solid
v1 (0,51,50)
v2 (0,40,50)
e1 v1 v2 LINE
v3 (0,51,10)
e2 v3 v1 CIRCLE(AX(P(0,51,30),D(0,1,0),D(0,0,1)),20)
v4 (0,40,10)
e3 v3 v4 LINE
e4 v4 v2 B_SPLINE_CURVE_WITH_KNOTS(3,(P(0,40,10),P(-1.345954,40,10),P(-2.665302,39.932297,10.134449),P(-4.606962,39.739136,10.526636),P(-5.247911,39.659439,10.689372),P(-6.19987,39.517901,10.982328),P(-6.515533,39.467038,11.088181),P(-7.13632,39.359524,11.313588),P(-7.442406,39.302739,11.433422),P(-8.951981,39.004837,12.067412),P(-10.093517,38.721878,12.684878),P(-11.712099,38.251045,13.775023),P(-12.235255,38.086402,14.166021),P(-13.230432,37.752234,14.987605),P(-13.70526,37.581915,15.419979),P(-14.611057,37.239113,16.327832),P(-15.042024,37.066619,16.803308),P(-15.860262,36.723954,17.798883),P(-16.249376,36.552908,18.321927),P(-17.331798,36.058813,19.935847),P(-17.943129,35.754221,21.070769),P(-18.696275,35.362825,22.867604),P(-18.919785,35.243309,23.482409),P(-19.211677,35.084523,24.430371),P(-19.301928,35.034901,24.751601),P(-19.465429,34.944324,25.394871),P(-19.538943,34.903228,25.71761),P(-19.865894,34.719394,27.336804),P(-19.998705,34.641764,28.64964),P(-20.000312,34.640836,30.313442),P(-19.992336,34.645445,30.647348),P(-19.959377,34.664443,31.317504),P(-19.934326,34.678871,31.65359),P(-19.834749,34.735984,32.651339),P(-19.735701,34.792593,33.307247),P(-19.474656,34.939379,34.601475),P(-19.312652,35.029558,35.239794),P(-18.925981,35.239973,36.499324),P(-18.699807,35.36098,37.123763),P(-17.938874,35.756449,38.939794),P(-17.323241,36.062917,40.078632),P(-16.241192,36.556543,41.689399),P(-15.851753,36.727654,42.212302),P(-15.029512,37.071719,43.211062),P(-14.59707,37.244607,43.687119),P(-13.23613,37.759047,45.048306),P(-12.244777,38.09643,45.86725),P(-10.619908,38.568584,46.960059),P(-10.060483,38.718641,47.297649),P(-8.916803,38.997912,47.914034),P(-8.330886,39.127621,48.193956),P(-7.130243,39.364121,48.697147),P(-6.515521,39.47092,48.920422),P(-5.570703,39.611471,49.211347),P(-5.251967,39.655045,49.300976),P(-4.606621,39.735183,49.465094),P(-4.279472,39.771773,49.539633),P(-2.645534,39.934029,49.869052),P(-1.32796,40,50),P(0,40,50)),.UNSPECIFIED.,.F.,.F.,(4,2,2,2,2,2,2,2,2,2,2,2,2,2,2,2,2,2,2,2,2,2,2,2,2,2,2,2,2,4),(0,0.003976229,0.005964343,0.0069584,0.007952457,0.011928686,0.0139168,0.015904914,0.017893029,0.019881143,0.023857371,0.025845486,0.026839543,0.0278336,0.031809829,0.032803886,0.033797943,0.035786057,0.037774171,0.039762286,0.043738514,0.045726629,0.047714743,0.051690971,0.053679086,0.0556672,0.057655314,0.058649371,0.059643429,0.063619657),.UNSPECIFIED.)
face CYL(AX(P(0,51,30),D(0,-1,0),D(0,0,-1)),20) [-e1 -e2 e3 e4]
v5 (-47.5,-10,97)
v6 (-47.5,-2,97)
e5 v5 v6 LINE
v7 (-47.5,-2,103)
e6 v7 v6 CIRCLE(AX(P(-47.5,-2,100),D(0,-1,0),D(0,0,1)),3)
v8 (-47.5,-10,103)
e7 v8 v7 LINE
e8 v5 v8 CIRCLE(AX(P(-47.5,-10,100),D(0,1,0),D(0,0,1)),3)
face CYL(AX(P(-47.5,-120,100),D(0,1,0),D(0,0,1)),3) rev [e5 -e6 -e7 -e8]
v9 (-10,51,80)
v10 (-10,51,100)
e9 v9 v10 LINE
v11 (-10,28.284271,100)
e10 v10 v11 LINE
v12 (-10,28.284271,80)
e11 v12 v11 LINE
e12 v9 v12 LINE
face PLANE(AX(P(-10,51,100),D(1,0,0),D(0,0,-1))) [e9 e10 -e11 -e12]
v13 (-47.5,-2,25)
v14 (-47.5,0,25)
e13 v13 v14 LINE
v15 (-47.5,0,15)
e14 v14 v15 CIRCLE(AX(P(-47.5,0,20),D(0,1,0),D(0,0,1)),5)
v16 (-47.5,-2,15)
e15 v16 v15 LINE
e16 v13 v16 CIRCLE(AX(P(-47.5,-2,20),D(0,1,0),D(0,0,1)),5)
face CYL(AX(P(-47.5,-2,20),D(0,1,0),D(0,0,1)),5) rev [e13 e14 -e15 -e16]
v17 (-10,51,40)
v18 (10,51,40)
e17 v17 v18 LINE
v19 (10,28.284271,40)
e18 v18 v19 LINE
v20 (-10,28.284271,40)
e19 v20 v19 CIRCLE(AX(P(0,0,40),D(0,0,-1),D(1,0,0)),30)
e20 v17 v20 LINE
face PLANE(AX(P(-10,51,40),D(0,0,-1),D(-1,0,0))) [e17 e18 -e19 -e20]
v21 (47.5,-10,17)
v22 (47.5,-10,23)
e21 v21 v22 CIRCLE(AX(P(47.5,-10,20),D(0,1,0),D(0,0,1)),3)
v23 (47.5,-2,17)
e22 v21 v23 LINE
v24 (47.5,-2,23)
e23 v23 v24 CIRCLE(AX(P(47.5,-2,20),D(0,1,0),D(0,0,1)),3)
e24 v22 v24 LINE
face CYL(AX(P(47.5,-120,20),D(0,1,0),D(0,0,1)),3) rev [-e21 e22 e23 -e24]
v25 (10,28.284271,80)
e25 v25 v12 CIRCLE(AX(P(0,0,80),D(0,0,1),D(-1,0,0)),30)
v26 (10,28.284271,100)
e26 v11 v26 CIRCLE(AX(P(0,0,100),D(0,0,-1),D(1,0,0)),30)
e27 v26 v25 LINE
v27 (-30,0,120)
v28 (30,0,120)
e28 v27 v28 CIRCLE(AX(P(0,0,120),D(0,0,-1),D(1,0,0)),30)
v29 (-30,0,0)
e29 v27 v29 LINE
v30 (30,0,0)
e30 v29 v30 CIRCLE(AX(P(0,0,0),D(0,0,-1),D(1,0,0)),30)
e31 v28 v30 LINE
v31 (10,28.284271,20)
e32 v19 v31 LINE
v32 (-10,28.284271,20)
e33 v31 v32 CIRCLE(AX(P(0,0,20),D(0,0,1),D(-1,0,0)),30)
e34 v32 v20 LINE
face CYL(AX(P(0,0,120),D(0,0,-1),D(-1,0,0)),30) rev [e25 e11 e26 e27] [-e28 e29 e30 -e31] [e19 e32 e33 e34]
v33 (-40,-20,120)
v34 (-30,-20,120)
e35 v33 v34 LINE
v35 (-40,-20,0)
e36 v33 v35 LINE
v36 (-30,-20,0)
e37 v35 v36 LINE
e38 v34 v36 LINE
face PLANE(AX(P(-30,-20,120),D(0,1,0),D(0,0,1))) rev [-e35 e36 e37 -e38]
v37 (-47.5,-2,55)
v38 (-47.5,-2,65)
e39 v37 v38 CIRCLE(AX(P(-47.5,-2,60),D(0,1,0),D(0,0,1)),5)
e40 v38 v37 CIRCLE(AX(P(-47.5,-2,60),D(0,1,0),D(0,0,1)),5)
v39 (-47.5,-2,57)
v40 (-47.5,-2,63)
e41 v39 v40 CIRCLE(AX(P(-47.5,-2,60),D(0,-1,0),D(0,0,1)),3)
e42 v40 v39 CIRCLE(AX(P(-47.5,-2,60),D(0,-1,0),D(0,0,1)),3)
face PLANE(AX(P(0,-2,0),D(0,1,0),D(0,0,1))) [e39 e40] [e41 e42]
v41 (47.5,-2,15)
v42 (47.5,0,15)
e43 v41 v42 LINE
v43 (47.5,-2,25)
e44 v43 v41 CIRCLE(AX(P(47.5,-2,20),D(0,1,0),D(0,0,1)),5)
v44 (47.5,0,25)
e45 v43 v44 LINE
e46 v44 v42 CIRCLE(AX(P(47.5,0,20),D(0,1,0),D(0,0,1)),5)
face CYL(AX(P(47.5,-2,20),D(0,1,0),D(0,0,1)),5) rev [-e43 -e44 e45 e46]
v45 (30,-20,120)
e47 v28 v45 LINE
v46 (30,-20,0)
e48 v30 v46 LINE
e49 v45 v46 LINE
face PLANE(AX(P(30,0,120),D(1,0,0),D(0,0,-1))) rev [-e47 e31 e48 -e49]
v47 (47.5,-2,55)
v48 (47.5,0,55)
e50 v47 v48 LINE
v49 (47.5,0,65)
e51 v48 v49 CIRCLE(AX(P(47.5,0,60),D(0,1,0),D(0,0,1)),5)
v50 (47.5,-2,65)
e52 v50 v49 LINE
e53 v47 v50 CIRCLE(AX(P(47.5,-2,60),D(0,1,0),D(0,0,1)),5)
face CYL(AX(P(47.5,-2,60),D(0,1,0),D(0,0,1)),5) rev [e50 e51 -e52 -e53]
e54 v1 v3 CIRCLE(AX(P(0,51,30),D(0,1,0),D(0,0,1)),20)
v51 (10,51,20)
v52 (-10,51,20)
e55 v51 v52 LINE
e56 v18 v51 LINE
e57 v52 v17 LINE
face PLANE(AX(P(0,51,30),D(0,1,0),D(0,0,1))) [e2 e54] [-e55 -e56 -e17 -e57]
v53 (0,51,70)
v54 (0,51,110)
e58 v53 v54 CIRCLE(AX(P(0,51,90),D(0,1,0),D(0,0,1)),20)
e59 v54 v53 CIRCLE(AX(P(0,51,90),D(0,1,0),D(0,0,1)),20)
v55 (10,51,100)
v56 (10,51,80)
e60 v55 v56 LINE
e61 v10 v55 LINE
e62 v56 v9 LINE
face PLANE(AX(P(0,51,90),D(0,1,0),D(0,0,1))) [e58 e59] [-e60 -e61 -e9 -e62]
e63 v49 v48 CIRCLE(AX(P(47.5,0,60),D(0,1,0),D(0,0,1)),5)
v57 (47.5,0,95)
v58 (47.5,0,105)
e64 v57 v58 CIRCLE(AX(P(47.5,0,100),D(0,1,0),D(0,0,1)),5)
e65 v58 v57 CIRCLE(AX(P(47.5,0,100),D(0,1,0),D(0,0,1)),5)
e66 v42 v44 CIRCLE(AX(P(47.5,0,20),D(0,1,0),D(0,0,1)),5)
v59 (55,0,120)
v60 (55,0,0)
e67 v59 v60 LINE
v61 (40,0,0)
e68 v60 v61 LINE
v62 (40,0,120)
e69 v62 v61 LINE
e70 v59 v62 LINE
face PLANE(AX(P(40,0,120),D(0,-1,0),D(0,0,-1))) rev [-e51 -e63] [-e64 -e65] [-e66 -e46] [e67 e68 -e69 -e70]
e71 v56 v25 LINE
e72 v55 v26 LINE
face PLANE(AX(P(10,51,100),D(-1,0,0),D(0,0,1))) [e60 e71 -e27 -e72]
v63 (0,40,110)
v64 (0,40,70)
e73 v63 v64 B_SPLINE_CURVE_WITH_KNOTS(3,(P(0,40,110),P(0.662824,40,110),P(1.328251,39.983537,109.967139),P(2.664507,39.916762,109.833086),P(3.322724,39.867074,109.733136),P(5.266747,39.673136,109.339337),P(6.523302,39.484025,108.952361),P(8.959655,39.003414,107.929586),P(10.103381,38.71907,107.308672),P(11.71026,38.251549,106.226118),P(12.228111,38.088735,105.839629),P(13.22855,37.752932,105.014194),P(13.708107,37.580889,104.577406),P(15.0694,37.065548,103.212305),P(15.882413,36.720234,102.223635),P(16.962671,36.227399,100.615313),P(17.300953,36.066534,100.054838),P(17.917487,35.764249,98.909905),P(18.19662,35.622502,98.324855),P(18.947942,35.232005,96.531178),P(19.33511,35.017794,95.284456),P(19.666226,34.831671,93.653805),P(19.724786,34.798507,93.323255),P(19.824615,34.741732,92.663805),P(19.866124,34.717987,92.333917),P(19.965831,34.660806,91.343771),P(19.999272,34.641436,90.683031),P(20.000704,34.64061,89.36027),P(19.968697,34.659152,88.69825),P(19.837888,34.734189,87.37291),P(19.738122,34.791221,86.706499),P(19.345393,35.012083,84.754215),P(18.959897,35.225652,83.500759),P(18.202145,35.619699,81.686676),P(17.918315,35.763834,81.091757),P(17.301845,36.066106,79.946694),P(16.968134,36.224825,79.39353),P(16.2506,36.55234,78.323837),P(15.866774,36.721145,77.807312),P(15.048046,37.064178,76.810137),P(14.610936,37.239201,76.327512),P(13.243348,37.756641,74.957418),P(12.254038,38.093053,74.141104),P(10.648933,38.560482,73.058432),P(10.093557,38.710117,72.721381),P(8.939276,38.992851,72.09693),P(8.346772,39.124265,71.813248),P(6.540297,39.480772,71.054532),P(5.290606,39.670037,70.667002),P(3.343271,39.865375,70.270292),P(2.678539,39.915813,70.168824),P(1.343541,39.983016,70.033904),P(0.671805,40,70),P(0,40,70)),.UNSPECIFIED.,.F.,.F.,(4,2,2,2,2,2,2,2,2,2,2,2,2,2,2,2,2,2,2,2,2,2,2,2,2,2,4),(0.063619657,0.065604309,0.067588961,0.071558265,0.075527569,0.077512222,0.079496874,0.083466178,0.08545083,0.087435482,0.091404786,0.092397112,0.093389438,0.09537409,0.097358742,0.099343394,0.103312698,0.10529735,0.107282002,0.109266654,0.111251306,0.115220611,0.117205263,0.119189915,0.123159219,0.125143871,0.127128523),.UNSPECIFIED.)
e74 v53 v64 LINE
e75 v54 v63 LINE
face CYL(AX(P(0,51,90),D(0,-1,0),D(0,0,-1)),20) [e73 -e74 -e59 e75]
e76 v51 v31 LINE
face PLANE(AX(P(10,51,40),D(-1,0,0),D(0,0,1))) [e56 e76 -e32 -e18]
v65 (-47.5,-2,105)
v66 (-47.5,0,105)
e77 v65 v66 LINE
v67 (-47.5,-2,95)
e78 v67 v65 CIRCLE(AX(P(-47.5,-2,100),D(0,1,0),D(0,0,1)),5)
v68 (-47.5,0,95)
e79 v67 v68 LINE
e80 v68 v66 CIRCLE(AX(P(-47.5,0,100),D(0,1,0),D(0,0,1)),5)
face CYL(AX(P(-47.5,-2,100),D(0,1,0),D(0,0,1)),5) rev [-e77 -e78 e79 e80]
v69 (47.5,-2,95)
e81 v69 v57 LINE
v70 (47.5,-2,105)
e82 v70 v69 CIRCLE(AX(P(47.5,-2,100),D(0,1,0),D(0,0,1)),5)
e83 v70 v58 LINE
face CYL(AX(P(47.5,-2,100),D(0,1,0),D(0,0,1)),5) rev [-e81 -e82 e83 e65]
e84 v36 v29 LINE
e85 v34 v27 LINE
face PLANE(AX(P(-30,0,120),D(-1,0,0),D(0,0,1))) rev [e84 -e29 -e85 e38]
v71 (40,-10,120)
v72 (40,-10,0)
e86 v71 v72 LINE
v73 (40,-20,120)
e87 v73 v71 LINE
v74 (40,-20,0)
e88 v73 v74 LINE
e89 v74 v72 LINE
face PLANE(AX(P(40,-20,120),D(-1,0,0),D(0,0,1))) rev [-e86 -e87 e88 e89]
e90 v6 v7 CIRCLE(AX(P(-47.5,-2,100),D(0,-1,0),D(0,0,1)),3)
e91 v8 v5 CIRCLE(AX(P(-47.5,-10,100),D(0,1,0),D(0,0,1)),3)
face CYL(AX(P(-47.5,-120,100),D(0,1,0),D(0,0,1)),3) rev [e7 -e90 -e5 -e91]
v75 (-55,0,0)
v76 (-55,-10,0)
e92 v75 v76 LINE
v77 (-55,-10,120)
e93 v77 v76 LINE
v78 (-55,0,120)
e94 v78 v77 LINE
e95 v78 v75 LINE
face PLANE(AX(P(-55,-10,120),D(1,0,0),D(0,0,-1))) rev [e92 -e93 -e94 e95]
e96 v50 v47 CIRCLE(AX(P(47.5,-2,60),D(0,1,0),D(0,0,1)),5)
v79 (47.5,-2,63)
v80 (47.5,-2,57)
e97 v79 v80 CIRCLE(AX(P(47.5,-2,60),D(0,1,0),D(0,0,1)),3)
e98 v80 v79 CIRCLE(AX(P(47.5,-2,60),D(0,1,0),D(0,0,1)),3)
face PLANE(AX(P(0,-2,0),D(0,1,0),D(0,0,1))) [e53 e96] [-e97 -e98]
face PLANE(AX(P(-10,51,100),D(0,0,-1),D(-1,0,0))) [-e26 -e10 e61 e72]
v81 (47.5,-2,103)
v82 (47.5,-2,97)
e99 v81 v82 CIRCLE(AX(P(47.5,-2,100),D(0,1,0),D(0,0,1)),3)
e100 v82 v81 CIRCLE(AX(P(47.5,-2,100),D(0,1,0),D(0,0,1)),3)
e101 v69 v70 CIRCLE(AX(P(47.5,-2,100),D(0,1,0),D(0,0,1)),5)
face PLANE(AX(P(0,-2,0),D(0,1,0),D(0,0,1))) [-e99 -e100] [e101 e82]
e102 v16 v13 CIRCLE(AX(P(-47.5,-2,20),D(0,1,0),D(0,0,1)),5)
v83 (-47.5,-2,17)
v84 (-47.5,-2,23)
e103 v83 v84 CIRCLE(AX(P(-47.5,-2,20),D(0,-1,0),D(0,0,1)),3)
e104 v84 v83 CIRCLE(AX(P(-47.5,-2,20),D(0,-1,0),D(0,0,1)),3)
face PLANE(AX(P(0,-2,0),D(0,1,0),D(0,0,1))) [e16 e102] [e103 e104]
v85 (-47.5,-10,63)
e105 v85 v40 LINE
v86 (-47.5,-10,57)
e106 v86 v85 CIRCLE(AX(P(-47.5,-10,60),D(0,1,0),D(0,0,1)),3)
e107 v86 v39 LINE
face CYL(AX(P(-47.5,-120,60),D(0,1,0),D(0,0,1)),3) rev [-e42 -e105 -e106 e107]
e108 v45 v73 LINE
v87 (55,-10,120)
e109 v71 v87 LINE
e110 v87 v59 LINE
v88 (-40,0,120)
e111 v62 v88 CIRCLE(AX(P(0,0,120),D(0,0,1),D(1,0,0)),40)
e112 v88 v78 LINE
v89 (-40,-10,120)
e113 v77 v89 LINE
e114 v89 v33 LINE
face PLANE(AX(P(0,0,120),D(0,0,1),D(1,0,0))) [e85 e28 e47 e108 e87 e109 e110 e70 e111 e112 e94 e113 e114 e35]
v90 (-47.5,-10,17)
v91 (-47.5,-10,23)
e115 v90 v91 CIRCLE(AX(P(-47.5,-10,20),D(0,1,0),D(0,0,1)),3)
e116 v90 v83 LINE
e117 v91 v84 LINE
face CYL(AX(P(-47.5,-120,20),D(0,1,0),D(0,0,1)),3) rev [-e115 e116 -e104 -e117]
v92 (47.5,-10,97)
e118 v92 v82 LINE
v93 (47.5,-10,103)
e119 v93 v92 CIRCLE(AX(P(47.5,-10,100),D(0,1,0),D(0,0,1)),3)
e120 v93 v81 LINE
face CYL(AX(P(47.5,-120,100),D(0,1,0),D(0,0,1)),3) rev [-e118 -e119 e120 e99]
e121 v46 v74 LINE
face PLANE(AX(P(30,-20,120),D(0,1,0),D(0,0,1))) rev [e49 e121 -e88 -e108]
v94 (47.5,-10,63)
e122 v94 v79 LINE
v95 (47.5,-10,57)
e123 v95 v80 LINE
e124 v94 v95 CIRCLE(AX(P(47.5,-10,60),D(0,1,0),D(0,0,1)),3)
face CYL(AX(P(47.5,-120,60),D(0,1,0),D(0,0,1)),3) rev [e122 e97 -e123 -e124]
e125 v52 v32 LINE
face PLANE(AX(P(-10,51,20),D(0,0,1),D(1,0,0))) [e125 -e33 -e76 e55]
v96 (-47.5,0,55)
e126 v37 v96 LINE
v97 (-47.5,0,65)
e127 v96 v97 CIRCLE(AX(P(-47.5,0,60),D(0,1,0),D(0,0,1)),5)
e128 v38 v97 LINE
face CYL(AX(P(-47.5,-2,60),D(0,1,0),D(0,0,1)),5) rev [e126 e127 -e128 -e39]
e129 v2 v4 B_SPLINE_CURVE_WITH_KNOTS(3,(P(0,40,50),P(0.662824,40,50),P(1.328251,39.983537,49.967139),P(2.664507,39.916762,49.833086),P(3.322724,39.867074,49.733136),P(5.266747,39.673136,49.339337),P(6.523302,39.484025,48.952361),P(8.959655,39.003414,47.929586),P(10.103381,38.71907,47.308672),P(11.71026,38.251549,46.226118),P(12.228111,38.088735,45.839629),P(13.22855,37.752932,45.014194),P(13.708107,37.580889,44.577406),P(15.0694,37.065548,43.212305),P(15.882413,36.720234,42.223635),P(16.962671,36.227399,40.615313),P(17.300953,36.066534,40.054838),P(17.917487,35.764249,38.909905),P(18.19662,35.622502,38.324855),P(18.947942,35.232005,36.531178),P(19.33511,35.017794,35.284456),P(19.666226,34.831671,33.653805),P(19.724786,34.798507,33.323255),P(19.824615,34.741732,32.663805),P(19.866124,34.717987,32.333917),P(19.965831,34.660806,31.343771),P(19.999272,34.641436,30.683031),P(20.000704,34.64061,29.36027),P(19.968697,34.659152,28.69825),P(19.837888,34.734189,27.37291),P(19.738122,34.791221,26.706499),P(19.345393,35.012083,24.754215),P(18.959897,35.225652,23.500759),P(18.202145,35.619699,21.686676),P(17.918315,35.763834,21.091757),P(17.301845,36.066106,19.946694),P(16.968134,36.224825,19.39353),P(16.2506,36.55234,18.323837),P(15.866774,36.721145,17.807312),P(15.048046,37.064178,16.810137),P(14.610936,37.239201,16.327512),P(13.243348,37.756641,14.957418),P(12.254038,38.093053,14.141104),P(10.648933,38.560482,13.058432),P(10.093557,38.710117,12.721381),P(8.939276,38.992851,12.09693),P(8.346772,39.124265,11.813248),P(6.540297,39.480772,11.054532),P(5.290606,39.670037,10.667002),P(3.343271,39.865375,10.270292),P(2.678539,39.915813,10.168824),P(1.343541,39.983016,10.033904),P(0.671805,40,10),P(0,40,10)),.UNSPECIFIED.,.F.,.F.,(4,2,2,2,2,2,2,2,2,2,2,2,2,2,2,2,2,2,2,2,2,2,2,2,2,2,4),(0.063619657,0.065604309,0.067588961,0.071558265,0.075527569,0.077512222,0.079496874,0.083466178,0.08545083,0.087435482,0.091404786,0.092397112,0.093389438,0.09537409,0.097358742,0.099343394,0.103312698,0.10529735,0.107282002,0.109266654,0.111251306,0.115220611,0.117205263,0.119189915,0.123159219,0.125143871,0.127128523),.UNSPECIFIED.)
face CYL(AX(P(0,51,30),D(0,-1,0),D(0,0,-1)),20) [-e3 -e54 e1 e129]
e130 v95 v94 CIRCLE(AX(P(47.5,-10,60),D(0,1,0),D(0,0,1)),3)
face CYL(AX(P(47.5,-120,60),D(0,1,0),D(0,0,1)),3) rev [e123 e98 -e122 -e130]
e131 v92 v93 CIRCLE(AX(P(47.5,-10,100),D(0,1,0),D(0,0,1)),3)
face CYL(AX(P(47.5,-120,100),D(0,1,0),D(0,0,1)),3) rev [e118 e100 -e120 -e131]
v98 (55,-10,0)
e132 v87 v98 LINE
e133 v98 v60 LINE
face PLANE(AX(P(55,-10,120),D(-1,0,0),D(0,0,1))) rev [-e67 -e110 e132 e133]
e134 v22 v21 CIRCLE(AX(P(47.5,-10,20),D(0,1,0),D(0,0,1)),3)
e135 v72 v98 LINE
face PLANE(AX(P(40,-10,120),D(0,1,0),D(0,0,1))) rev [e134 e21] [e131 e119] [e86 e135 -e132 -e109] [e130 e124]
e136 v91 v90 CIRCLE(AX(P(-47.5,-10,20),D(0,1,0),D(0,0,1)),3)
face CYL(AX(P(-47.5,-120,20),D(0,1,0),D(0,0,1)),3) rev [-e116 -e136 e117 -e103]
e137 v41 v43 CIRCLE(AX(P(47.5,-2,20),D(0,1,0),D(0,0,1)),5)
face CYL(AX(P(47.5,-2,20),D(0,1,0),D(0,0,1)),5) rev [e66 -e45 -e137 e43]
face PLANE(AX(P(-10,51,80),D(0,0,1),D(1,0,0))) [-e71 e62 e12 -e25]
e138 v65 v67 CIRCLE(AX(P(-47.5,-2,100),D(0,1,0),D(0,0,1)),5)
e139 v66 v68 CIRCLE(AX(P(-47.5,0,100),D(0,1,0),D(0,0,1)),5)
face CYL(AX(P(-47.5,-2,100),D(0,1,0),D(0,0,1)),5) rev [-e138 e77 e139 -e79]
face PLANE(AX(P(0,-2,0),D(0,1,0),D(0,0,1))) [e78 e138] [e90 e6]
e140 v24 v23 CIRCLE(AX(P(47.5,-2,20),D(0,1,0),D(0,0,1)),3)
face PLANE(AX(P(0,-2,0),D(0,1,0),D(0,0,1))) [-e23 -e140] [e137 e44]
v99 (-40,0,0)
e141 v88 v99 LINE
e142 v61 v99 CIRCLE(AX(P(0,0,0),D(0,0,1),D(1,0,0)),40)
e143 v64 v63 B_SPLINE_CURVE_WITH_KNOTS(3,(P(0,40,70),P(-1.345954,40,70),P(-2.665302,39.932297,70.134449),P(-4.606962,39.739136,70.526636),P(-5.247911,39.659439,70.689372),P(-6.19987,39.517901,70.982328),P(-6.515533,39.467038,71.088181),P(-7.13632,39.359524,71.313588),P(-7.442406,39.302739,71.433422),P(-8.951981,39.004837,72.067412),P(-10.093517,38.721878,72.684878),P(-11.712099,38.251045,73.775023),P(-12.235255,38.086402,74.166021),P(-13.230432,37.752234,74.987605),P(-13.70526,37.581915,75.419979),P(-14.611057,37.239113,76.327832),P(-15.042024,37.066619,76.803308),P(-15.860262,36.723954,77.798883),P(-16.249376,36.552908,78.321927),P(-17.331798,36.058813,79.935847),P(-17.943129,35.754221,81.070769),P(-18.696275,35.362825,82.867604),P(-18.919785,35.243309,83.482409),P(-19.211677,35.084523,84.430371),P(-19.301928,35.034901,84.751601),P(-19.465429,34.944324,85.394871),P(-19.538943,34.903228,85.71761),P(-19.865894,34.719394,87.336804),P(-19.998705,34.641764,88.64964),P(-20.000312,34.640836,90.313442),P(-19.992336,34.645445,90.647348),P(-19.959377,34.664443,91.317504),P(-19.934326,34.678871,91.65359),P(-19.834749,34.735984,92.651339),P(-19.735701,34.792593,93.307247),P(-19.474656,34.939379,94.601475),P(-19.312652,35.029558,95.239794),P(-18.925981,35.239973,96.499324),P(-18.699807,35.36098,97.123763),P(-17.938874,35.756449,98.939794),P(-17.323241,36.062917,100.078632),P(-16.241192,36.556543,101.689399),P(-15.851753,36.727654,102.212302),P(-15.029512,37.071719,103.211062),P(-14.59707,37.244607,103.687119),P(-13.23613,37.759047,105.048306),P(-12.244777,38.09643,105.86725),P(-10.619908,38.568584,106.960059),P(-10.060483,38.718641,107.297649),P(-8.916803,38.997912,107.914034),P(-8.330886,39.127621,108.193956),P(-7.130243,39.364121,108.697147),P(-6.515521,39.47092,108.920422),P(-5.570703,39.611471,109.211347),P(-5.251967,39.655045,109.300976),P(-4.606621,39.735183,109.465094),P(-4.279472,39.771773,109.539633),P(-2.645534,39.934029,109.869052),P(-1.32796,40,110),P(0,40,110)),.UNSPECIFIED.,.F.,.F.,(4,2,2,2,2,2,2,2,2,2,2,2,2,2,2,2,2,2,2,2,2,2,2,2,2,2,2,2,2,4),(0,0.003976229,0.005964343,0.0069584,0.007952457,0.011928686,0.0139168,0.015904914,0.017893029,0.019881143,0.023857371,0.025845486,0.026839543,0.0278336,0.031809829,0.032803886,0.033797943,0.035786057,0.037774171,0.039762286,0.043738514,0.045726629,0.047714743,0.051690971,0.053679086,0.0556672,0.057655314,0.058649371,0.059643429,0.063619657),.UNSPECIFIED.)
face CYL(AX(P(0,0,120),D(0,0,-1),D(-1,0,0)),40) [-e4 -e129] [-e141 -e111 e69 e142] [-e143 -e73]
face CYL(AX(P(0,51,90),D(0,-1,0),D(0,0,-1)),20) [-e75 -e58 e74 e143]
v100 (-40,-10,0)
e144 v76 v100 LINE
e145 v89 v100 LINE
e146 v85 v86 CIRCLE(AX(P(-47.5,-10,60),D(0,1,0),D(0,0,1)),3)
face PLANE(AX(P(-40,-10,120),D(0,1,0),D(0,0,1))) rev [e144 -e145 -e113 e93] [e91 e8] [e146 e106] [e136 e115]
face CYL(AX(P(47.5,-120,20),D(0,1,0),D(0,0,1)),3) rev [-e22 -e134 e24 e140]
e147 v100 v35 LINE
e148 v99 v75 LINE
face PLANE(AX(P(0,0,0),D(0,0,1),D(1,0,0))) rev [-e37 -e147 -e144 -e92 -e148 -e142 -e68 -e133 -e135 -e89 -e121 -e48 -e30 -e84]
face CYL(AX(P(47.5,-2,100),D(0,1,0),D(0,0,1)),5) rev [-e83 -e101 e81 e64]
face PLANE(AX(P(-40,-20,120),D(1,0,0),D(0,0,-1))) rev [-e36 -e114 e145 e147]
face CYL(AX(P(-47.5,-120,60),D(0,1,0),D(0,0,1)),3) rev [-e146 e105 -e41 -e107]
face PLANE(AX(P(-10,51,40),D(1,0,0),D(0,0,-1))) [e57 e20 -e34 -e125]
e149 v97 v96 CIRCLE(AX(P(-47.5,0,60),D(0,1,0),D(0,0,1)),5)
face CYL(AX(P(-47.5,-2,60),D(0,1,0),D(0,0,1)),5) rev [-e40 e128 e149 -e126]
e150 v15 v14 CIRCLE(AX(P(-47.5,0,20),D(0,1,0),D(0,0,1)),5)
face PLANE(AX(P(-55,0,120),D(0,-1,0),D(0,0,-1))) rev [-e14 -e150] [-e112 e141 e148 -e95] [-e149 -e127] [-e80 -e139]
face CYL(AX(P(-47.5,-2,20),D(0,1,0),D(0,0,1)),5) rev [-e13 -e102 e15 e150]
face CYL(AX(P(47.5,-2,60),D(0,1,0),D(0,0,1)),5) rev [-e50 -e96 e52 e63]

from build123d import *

# Parameters (mm, degrees)
HALF_PIPE_CAP_BODY_DEPTH     = 120
MOUNTING_HOLES_SKETCH_R      = 3
MOUNTING_HOLES_6X_6_DEPTH    = 120
COUNTERBORE_SKETCH_R         = 5
COUNTERBORE_SKETCH_R_2       = 3
COUNTERBORES_6X_10X2_DEPTH   = 2
BOSS_SKETCH_R                = 20
BOSS_SKETCH_W                = 20
BOSS_SKETCH_H                = 20
TOP_BOSSES_2X_40_DEPTH       = 20
SQUARE_SOCKET_SKETCH_W       = 20
SQUARE_SOCKET_SKETCH_H       = 20
SQUARE_SOCKETS_2X20X20_DEPTH = 20


with BuildPart() as part:
    # Cap Profile Sketch → Half Pipe Cap Body (new body)
    with BuildSketch(Plane.XY):
        with BuildLine():
            Line((-55, 0), (-40, 0))
            ThreePointArc((-40, 0), (0, 40), (40, 0))
            Line((40, 0), (55, 0))
            Line((55, 0), (55, -10))
            Line((55, -10), (40, -10))
            Line((40, -10), (40, -20))
            Line((40, -20), (30, -20))
            Line((30, -20), (30, 0))
            ThreePointArc((30, 0), (0, 30), (-30, 0))
            Line((-30, 0), (-30, -20))
            Line((-30, -20), (-40, -20))
            Line((-40, -20), (-40, -10))
            Line((-40, -10), (-55, -10))
            Line((-55, -10), (-55, 0))
        make_face()
    extrude(amount=HALF_PIPE_CAP_BODY_DEPTH)

    # Mounting Holes Sketch → Mounting Holes 6xØ6 (cut)
    with BuildSketch(Plane(origin=(0, 0, 0), x_dir=(1, 0, 0), z_dir=(0, 1, 0))):
        with Locations(Location((-47.5, -20, 0), (0, 0, 270))):
            Circle(MOUNTING_HOLES_SKETCH_R)
        with Locations(Location((-47.5, -100, 0), (0, 0, 270))):
            Circle(MOUNTING_HOLES_SKETCH_R)
        with Locations(Location((-47.5, -60, 0), (0, 0, 270))):
            Circle(MOUNTING_HOLES_SKETCH_R)
        with Locations(Location((47.5, -20, 0), (0, 0, 270))):
            Circle(MOUNTING_HOLES_SKETCH_R)
        with Locations(Location((47.5, -60, 0), (0, 0, 270))):
            Circle(MOUNTING_HOLES_SKETCH_R)
        with Locations(Location((47.5, -100, 0), (0, 0, 270))):
            Circle(MOUNTING_HOLES_SKETCH_R)
    extrude(amount=-MOUNTING_HOLES_6X_6_DEPTH, mode=Mode.SUBTRACT)

    # Counterbore Sketch → Counterbores 6xØ10x2 (cut)
    # profile 1 of 6: a face of its own
    with BuildSketch(Plane(origin=(0, 0, 0), x_dir=(1, 0, 0), z_dir=(0, 1, 0))):
        with Locations(Location((-47.5, -60, 0), (0, 0, 270))):
            Circle(COUNTERBORE_SKETCH_R)
        with Locations(Location((-47.5, -60, 0), (0, 0, 270))):
            Circle(COUNTERBORE_SKETCH_R_2, mode=Mode.SUBTRACT)
    # profile 2 of 6: a face of its own
    with BuildSketch(Plane(origin=(0, 0, 0), x_dir=(1, 0, 0), z_dir=(0, 1, 0))):
        with Locations(Location((-47.5, -100, 0), (0, 0, 270))):
            Circle(COUNTERBORE_SKETCH_R)
        with Locations(Location((-47.5, -100, 0), (0, 0, 270))):
            Circle(COUNTERBORE_SKETCH_R_2, mode=Mode.SUBTRACT)
    # profile 3 of 6: a face of its own
    with BuildSketch(Plane(origin=(0, 0, 0), x_dir=(1, 0, 0), z_dir=(0, 1, 0))):
        with Locations(Location((-47.5, -20, 0), (0, 0, 270))):
            Circle(COUNTERBORE_SKETCH_R)
        with Locations(Location((-47.5, -20, 0), (0, 0, 270))):
            Circle(COUNTERBORE_SKETCH_R_2, mode=Mode.SUBTRACT)
    # profile 4 of 6: a face of its own
    with BuildSketch(Plane(origin=(0, 0, 0), x_dir=(1, 0, 0), z_dir=(0, 1, 0))):
        with Locations(Location((47.5, -20, 0), (0, 0, 270))):
            Circle(COUNTERBORE_SKETCH_R)
        with Locations(Location((47.5, -20, 0), (0, 0, 270))):
            Circle(COUNTERBORE_SKETCH_R_2, mode=Mode.SUBTRACT)
    # profile 5 of 6: a face of its own
    with BuildSketch(Plane(origin=(0, 0, 0), x_dir=(1, 0, 0), z_dir=(0, 1, 0))):
        with Locations(Location((47.5, -60, 0), (0, 0, 270))):
            Circle(COUNTERBORE_SKETCH_R)
        with Locations(Location((47.5, -60, 0), (0, 0, 270))):
            Circle(COUNTERBORE_SKETCH_R_2, mode=Mode.SUBTRACT)
    # profile 6 of 6: a face of its own
    with BuildSketch(Plane(origin=(0, 0, 0), x_dir=(1, 0, 0), z_dir=(0, 1, 0))):
        with Locations(Location((47.5, -100, 0), (0, 0, 270))):
            Circle(COUNTERBORE_SKETCH_R)
        with Locations(Location((47.5, -100, 0), (0, 0, 270))):
            Circle(COUNTERBORE_SKETCH_R_2, mode=Mode.SUBTRACT)
    extrude(amount=-COUNTERBORES_6X_10X2_DEPTH, mode=Mode.SUBTRACT)

    # Boss Sketch → Top Bosses 2xØ40 (add)
    # profile 1 of 2: a face of its own
    with BuildSketch(Plane(origin=(0, 31, 0), x_dir=(1, 0, 0), z_dir=(0, 1, 0))):
        with Locations(Location((0, -30, 0), (0, 0, 90))):
            Circle(BOSS_SKETCH_R)
        with Locations((0, -30)):
            Rectangle(BOSS_SKETCH_W, BOSS_SKETCH_H, mode=Mode.SUBTRACT)
    # profile 2 of 2: a face of its own
    with BuildSketch(Plane(origin=(0, 31, 0), x_dir=(1, 0, 0), z_dir=(0, 1, 0))):
        with Locations(Location((0, -90, 0), (0, 0, 90))):
            Circle(BOSS_SKETCH_R)
        with Locations((0, -90)):
            Rectangle(BOSS_SKETCH_W, BOSS_SKETCH_H, mode=Mode.SUBTRACT)
    extrude(amount=TOP_BOSSES_2X_40_DEPTH)

    # Square Socket Sketch → Square Sockets 2x20x20 (cut, symmetric)
    with BuildSketch(Plane(origin=(0, 31, 0), x_dir=(1, 0, 0), z_dir=(0, 1, 0))):
        with Locations((0, -30)):
            Rectangle(SQUARE_SOCKET_SKETCH_W, SQUARE_SOCKET_SKETCH_H)
        with Locations((0, -90)):
            Rectangle(SQUARE_SOCKET_SKETCH_W, SQUARE_SOCKET_SKETCH_H)
    extrude(amount=SQUARE_SOCKETS_2X20X20_DEPTH, both=True, mode=Mode.SUBTRACT)


solid = part.part
